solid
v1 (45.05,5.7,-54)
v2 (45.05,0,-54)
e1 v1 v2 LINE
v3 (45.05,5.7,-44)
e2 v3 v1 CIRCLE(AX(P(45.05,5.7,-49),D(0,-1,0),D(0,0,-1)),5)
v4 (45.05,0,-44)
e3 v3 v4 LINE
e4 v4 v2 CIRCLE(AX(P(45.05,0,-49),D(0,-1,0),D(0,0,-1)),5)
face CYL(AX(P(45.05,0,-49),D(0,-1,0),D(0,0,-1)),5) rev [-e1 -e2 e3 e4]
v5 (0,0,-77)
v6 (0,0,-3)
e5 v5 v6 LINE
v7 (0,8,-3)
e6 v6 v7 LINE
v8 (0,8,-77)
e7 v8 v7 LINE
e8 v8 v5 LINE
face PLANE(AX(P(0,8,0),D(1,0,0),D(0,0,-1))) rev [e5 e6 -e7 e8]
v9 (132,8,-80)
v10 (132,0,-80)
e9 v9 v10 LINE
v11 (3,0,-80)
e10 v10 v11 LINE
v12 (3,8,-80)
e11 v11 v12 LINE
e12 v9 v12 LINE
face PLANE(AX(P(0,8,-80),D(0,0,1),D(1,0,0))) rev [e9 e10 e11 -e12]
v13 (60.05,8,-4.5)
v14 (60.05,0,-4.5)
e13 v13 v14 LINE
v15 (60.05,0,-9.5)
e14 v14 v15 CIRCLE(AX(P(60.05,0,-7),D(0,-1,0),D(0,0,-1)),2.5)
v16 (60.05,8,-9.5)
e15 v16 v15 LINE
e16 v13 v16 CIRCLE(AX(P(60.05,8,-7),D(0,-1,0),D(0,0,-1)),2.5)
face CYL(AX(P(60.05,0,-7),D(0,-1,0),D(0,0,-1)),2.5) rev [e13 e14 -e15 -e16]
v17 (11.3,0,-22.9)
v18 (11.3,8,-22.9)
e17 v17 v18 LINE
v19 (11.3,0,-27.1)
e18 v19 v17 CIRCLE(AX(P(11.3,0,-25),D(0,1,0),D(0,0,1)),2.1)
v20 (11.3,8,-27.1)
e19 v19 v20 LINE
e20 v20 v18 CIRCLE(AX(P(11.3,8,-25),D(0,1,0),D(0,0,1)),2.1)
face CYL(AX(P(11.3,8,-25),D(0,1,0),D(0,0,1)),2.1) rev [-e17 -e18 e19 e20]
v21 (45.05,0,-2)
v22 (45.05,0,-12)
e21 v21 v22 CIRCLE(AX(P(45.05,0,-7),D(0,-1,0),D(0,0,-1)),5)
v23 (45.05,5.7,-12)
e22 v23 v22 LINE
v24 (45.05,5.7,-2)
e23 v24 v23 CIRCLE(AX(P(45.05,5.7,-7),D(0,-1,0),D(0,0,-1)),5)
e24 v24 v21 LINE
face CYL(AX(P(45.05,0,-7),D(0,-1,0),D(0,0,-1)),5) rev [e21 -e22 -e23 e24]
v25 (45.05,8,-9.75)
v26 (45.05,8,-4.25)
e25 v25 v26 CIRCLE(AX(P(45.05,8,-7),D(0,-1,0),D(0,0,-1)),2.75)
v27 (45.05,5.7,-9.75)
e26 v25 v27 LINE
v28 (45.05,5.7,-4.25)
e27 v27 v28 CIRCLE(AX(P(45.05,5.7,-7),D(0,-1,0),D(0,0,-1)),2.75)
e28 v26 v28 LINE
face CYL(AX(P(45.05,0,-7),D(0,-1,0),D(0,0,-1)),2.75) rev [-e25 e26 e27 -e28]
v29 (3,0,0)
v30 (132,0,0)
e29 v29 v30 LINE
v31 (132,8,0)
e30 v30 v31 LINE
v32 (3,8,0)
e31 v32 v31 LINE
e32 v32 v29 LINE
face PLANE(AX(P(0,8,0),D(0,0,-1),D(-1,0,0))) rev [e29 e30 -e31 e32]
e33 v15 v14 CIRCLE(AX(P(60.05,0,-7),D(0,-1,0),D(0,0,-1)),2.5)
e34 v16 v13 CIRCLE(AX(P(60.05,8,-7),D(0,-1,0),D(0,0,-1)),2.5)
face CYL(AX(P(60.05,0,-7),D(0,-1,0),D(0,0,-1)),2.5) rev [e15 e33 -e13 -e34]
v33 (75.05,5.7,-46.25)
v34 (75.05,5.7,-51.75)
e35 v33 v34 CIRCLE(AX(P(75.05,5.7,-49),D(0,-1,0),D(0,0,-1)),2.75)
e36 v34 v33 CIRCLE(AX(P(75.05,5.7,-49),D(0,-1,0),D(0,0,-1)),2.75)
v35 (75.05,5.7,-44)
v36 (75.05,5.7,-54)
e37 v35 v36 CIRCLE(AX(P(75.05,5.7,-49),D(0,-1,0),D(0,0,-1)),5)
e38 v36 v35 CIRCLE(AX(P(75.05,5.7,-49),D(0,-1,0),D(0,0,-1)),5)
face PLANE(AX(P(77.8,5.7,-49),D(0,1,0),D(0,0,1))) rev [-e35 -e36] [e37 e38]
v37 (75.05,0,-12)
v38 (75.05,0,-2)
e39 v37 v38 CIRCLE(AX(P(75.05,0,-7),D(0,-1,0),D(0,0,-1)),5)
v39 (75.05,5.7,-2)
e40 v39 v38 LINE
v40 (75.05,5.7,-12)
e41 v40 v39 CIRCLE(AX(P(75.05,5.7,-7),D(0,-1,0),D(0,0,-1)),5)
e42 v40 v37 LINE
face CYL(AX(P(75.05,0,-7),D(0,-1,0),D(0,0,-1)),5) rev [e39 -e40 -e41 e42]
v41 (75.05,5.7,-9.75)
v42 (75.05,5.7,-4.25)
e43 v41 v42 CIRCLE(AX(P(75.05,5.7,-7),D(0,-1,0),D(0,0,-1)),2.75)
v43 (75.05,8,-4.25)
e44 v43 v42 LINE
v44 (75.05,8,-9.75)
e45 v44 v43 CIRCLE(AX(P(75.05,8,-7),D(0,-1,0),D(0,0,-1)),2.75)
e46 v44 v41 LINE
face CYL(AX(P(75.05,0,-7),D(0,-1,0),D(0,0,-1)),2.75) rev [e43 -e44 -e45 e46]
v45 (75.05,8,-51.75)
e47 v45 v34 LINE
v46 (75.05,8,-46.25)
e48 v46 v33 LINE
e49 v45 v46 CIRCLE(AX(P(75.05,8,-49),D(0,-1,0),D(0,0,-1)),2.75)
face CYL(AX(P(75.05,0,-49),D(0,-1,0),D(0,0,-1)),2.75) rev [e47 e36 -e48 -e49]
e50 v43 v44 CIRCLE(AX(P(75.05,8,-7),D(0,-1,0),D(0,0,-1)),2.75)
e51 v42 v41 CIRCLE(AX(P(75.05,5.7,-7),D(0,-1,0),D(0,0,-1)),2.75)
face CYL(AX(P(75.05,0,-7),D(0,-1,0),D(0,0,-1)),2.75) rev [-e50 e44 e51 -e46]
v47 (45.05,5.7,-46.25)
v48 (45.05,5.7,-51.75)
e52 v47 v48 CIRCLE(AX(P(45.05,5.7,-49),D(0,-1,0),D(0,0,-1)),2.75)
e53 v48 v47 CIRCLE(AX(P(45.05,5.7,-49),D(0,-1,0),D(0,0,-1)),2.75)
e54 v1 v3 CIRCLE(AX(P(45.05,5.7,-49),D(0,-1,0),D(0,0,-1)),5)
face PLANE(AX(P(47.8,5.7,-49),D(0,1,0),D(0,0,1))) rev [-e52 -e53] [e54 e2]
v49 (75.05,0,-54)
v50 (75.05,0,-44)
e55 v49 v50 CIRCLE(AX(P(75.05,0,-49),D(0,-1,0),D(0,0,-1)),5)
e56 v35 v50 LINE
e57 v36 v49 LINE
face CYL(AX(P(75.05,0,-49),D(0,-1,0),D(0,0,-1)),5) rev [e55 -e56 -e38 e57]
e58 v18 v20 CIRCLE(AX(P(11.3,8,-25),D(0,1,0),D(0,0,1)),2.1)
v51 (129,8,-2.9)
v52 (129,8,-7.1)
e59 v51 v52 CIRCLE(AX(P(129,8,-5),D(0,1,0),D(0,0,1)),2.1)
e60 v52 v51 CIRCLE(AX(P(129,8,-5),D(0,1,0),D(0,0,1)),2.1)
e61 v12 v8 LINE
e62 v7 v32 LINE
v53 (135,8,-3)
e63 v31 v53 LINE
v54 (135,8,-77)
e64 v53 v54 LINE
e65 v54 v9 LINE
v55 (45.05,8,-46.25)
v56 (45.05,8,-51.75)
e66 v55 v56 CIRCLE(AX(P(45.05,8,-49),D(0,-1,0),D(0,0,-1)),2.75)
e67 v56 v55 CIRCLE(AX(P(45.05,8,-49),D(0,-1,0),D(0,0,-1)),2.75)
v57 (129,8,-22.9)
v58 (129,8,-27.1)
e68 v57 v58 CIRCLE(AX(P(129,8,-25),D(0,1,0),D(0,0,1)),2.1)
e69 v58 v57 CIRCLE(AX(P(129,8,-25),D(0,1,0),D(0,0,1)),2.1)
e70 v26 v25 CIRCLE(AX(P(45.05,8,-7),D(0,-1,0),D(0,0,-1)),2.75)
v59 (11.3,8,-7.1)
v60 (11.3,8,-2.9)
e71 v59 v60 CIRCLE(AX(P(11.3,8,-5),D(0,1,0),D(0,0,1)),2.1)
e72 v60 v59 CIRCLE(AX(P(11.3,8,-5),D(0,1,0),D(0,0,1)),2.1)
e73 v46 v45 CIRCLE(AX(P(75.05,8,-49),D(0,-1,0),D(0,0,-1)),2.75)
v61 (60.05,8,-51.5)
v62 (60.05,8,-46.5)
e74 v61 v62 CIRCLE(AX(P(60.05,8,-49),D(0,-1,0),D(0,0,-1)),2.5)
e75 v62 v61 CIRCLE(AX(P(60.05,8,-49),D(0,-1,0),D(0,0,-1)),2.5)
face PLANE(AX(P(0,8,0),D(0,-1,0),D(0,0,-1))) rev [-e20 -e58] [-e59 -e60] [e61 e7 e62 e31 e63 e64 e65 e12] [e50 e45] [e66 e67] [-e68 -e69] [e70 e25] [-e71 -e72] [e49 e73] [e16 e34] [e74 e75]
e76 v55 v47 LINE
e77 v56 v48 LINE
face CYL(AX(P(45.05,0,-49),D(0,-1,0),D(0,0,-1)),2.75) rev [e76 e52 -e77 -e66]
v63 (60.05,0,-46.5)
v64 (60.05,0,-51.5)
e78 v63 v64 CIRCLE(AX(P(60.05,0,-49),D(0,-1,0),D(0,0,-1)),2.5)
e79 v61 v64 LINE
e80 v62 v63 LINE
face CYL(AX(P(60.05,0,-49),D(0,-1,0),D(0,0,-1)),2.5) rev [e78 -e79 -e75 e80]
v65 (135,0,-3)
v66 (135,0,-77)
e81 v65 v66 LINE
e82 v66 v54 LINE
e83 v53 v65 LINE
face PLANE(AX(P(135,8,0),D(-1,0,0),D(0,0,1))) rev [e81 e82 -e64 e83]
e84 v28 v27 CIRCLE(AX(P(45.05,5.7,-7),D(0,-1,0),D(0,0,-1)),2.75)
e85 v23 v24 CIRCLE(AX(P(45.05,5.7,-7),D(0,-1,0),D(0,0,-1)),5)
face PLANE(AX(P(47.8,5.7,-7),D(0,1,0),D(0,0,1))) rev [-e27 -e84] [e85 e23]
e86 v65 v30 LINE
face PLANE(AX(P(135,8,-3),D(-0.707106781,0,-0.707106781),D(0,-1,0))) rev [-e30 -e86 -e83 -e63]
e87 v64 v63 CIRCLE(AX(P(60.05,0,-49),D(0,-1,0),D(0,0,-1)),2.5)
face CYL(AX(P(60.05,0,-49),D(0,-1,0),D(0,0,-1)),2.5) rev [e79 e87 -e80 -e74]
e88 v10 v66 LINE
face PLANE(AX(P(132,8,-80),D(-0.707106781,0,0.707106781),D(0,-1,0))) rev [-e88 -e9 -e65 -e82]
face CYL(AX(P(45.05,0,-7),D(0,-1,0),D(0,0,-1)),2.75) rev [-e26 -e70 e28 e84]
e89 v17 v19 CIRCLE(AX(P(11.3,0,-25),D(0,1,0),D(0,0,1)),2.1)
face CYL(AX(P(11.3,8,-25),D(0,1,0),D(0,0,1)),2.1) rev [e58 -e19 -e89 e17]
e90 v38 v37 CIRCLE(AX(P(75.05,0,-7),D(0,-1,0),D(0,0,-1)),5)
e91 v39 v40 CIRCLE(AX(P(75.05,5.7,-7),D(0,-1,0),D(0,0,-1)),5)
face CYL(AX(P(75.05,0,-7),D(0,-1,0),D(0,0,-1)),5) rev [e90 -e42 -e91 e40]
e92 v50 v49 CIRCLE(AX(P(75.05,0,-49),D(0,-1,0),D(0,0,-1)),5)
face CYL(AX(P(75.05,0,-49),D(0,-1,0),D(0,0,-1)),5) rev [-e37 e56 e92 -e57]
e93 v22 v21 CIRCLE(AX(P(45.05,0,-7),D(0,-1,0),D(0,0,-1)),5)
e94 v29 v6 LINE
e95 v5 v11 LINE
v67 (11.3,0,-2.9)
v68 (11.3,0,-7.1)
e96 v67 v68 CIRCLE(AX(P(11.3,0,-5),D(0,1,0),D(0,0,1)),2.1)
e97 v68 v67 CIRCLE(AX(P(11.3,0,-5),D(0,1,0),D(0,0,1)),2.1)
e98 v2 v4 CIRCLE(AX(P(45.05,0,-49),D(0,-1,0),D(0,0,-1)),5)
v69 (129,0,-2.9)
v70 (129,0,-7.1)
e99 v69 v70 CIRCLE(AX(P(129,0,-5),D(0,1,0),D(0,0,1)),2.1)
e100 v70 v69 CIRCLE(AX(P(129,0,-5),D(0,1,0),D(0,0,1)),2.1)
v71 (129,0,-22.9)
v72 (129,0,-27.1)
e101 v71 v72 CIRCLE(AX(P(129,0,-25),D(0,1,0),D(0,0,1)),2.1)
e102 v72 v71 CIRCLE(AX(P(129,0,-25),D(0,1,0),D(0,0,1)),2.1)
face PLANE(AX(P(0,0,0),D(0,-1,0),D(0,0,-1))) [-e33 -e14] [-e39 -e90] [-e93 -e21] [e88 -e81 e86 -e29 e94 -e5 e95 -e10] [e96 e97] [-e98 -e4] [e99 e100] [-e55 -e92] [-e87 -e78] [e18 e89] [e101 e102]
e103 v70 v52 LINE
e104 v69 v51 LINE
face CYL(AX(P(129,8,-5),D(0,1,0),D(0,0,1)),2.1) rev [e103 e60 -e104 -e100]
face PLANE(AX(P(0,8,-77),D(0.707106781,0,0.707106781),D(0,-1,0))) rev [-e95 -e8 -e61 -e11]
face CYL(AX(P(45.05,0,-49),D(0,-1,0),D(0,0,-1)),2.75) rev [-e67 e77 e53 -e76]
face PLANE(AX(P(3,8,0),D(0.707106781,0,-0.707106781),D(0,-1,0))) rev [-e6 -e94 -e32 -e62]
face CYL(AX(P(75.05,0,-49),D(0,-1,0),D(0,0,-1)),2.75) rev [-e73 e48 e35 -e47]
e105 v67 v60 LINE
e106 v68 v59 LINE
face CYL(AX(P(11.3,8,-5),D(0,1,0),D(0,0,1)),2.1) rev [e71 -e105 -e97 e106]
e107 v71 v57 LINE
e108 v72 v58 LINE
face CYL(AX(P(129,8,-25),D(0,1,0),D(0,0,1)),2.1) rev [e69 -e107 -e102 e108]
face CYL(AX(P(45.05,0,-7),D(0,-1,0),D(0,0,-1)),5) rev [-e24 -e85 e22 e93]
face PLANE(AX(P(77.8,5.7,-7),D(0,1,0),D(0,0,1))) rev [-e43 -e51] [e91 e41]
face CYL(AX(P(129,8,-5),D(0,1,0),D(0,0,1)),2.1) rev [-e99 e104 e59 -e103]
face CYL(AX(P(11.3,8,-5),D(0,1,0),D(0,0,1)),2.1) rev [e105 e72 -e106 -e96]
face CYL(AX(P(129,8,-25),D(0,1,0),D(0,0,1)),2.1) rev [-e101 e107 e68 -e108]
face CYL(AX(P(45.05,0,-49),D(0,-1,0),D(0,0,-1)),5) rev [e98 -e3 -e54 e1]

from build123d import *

# Parameters (mm, degrees)
SKETCH1_W                                            = 135
SKETCH1_H                                            = 80
BOSS_EXTRUDE1_DEPTH                                  = 8
CBORE_FOR_M5_HEXAGON_SOCKET_HEAD_CAP_SCR_D           = 5.5
CBORE_FOR_M5_HEXAGON_SOCKET_HEAD_CAP_SCR_CBORE_D     = 10
CBORE_FOR_M5_HEXAGON_SOCKET_HEAD_CAP_SCR_CBORE_DEPTH = 5.7
M5_TAPPED_HOLE1_D                                    = 4.2
CHAMFER1_SIZE                                        = 3
F_5_0MM_DOWEL_HOLE1_D                                = 5


with BuildPart() as part:
    # Sketch1 → Boss-Extrude1 (new body)
    with BuildSketch(Plane(origin=(0, 0, 0), x_dir=(1, 0, 0), z_dir=(0, 1, 0))):
        with Locations((67.5, 40)):
            Rectangle(SKETCH1_W, SKETCH1_H)
    extrude(amount=BOSS_EXTRUDE1_DEPTH)

    # CBORE for M5 Hexagon socket head cap screws1 (through all)
    with Locations(Plane(origin=(0, 0, 0), x_dir=(-1, 0, 0), z_dir=(0, -1, 0))):
        with Locations((-75.05, 49), (-45.05, 49), (-45.05, 7), (-75.05, 7)):
            CounterBoreHole(CBORE_FOR_M5_HEXAGON_SOCKET_HEAD_CAP_SCR_D / 2, CBORE_FOR_M5_HEXAGON_SOCKET_HEAD_CAP_SCR_CBORE_D / 2, CBORE_FOR_M5_HEXAGON_SOCKET_HEAD_CAP_SCR_CBORE_DEPTH)

    # M5 Tapped Hole1 (through all)
    with Locations(Plane(origin=(0, 8, 0), x_dir=(1, 0, 0), z_dir=(0, 1, 0))):
        with Locations((129, 25), (129, 5), (11.3, 25), (11.3, 5)):
            Hole(M5_TAPPED_HOLE1_D / 2)

    # Chamfer1
    chamfer1_edges = [part.edges().sort_by_distance(p)[0] for p in [
        (0, 4, -80),
        (135, 4, -80),
        (135, 4, 0),
        (0, 4, 0),
    ]]
    chamfer(chamfer1_edges, length=CHAMFER1_SIZE)

    # Ø5.0mm Dowel Hole1 (through all)
    with Locations(Plane(origin=(0, 0, 0), x_dir=(-1, 0, 0), z_dir=(0, -1, 0))):
        with Locations((-60.05, 7), (-60.05, 49)):
            Hole(F_5_0MM_DOWEL_HOLE1_D / 2)


solid = part.part
